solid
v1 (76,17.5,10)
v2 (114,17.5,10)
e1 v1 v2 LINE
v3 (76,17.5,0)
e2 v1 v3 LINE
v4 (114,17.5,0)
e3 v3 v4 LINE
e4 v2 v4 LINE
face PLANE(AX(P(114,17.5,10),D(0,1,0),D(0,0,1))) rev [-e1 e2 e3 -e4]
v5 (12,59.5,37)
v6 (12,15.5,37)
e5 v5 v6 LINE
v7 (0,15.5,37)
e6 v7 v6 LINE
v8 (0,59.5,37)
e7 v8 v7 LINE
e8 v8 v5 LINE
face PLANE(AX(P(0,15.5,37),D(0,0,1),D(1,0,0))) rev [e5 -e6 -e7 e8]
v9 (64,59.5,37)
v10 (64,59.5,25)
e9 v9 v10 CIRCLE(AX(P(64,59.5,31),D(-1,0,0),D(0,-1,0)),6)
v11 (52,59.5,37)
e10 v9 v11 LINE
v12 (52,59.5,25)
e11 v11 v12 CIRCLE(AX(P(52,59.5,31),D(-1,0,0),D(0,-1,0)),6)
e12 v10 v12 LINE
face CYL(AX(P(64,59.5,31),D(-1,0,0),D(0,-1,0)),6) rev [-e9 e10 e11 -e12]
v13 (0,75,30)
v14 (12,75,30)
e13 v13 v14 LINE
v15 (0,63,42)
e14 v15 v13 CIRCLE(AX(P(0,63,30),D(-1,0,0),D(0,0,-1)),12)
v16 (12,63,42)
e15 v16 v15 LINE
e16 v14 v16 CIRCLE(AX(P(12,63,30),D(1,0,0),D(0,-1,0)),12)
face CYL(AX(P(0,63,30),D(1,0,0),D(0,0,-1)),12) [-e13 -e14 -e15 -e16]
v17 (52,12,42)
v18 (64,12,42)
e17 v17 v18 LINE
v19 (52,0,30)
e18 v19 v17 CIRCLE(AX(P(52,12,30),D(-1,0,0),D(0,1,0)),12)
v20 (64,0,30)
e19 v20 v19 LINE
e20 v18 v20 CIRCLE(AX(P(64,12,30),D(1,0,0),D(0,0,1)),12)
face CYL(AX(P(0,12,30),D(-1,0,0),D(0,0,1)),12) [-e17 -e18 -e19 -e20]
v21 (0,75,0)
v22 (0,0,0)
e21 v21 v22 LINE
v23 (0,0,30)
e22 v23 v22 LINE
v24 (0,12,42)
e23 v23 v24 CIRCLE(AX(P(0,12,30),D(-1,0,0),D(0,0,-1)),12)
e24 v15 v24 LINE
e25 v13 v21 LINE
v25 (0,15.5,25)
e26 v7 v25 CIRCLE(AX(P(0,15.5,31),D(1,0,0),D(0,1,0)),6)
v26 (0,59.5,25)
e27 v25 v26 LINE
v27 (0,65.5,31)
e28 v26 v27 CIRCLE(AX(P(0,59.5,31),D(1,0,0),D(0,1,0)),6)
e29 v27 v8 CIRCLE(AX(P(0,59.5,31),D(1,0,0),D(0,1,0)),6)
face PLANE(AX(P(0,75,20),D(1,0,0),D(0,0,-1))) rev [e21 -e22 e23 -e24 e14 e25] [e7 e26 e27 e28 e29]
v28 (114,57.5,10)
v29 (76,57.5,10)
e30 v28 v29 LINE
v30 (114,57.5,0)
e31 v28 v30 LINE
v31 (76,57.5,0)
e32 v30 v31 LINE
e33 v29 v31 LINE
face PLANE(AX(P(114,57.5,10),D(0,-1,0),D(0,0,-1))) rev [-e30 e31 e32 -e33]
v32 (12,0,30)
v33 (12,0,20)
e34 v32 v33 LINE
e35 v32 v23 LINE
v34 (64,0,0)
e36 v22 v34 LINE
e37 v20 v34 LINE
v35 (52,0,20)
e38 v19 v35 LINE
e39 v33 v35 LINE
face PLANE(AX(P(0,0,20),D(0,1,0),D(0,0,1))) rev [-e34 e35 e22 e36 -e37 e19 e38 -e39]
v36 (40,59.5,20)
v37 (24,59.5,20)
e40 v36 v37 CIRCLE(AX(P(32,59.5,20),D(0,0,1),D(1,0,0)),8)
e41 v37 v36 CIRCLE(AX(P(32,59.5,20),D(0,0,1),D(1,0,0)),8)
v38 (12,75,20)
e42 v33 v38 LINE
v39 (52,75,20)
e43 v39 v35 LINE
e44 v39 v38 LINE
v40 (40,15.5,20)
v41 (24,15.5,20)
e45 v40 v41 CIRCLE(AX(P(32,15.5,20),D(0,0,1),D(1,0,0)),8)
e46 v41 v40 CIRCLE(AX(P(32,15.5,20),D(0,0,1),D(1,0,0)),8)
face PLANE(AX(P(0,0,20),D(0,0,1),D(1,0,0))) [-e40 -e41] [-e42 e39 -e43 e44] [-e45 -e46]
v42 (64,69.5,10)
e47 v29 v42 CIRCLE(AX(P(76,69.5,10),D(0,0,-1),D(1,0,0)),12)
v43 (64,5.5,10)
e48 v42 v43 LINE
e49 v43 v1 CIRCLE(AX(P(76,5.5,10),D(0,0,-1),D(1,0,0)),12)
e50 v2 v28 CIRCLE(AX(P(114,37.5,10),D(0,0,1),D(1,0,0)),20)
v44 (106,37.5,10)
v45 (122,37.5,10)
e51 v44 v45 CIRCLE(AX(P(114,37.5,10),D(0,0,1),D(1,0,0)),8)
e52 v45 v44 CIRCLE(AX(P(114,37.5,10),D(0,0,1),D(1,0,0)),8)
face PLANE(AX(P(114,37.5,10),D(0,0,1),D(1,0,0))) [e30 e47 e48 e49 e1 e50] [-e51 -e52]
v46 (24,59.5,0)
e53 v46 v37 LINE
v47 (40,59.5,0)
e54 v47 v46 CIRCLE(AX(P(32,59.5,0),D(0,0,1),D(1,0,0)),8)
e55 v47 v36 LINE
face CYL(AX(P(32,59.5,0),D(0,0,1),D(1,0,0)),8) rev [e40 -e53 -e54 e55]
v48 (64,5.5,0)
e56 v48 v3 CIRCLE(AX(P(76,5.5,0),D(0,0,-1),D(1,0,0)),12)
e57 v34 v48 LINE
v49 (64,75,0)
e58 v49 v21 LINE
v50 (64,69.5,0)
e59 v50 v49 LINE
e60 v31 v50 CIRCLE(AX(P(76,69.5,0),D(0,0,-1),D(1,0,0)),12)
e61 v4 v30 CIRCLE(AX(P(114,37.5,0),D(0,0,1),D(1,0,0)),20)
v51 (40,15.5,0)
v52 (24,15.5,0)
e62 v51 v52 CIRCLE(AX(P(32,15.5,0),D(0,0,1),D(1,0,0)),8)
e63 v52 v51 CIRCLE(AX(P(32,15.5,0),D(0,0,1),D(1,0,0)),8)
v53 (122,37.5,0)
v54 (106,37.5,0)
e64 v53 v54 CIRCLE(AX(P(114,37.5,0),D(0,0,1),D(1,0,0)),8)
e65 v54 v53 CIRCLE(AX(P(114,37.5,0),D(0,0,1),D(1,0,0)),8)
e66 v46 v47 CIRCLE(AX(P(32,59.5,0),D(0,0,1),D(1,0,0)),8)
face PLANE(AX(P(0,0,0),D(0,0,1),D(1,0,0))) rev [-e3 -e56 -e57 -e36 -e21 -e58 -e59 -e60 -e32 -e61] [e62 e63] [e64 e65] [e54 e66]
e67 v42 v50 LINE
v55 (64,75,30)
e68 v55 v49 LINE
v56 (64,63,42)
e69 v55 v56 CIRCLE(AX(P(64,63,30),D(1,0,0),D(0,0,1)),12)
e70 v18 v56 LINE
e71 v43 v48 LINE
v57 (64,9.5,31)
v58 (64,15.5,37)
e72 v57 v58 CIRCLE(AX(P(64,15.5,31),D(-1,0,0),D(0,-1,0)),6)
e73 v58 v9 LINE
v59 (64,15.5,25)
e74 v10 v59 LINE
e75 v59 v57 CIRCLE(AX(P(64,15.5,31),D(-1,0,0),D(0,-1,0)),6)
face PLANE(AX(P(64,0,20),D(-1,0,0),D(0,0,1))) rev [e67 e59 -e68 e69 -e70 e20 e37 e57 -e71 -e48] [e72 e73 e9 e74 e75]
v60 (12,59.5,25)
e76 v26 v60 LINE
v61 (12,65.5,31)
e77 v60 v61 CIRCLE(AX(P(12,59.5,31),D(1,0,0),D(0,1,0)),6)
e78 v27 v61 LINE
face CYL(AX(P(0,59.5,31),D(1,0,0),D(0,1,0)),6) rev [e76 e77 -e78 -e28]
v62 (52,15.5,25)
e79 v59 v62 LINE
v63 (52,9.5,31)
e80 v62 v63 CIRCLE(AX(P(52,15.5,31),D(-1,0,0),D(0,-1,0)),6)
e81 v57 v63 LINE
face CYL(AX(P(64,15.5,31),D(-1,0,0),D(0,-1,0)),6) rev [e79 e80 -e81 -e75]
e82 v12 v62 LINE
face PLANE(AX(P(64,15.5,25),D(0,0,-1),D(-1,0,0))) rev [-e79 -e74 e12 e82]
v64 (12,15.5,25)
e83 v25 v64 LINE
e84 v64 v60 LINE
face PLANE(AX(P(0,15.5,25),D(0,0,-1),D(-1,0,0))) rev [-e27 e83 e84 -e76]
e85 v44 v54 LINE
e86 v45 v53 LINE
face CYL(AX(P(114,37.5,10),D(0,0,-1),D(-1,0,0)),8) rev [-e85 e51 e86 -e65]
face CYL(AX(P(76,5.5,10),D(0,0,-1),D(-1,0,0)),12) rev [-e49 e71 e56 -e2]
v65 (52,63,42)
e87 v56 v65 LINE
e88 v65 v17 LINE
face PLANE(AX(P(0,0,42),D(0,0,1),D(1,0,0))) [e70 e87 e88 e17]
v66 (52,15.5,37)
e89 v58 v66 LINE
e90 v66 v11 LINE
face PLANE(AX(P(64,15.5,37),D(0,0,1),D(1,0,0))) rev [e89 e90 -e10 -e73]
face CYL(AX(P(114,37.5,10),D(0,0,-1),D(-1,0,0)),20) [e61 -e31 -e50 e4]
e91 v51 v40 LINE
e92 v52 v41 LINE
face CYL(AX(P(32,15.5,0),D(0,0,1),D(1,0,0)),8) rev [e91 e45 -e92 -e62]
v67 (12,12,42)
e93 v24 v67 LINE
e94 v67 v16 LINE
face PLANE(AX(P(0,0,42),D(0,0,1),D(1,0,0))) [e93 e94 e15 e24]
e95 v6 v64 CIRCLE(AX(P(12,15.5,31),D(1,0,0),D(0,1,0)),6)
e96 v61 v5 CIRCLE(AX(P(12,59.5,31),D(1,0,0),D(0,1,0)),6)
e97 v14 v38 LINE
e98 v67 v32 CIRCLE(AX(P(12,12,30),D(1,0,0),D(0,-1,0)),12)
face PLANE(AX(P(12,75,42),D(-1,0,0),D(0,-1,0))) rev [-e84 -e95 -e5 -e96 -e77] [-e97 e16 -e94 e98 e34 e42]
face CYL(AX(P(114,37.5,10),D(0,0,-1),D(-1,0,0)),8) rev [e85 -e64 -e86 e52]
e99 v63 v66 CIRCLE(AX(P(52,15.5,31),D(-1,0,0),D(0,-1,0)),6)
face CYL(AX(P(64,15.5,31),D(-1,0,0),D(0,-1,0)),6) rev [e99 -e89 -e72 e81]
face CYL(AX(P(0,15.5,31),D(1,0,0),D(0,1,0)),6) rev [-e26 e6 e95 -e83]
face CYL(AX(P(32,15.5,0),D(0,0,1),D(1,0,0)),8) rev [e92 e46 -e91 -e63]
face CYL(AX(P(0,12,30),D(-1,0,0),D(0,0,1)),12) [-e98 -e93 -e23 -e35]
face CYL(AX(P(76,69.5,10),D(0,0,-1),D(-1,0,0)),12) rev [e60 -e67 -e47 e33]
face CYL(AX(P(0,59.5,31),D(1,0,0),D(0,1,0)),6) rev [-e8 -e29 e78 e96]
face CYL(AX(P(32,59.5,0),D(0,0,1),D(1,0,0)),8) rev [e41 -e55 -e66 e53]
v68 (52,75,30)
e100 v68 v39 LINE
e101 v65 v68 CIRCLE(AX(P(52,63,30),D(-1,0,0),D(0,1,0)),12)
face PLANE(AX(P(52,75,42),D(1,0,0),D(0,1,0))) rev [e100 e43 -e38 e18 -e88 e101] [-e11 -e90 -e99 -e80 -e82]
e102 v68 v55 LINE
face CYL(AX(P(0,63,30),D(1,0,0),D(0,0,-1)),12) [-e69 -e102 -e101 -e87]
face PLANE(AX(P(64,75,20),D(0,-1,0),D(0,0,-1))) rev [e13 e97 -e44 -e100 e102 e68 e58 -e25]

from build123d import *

# Parameters (mm, degrees)
BASE_BLOCK_SKETCH_W     = 64
BASE_BLOCK_SKETCH_H     = 75
BASE_BLOCK_DEPTH        = 20
CLAMP_LUG_A_SKETCH_W    = 12
CLAMP_LUG_A_SKETCH_H    = 75
CLAMP_LUG_A_DEPTH       = 22
CLAMP_LUG_B_SKETCH_W    = 12
CLAMP_LUG_B_SKETCH_H    = 75
CLAMP_LUG_B_DEPTH       = 22
ADJUSTMENT_SLOT_A_DEPTH = 101.463923873
ADJUSTMENT_SLOT_B_DEPTH = 101.463923873
MOUNTING_TAB_SKETCH_R   = 8
MOUNTING_TAB_DEPTH      = 10
BACK_WALL_CUT_SKETCH_R  = 8
BACK_WALL_CUT_DEPTH     = 156.128978595
LUG_A_EDGE_FILLET_R12_R = 12
LUG_B_EDGE_FILLET_R12_R = 12


with BuildPart() as part:
    # Base Block Sketch → Base Block (new body)
    with BuildSketch(Plane.XY):
        with Locations((32, 37.5)):
            Rectangle(BASE_BLOCK_SKETCH_W, BASE_BLOCK_SKETCH_H)
    extrude(amount=BASE_BLOCK_DEPTH)

    # Clamp Lug A Sketch → Clamp Lug A (add)
    with BuildSketch(Plane.XY.offset(20)):
        with Locations((6, 37.5)):
            Rectangle(CLAMP_LUG_A_SKETCH_W, CLAMP_LUG_A_SKETCH_H)
    extrude(amount=CLAMP_LUG_A_DEPTH)

    # Clamp Lug B Sketch → Clamp Lug B (add)
    with BuildSketch(Plane.XY.offset(20)):
        with Locations((58, 37.5)):
            Rectangle(CLAMP_LUG_B_SKETCH_W, CLAMP_LUG_B_SKETCH_H)
    extrude(amount=CLAMP_LUG_B_DEPTH)

    # Adjustment Slot A Sketch → Adjustment Slot A (cut, through all)
    with BuildSketch(Plane(origin=(12, 0, 0), x_dir=(0, 0, -1), z_dir=(1, 0, 0))):
        with BuildLine():
            Line((-37, 15.5), (-37, 59.5))
            ThreePointArc((-37, 59.5), (-31, 65.5), (-25, 59.5))
            Line((-25, 59.5), (-25, 15.5))
            ThreePointArc((-25, 15.5), (-31, 9.5), (-37, 15.5))
        make_face()
    extrude(amount=-ADJUSTMENT_SLOT_A_DEPTH, mode=Mode.SUBTRACT)

    # Adjustment Slot B Sketch → Adjustment Slot B (cut, through all)
    with BuildSketch(Plane.ZY.offset(-52)):
        with BuildLine():
            Line((25, 15.5), (25, 59.5))
            ThreePointArc((25, 59.5), (31, 65.5), (37, 59.5))
            Line((37, 59.5), (37, 15.5))
            ThreePointArc((37, 15.5), (31, 9.5), (25, 15.5))
        make_face()
    extrude(amount=-ADJUSTMENT_SLOT_B_DEPTH, mode=Mode.SUBTRACT)

    # Mounting Tab Sketch → Mounting Tab (add)
    with BuildSketch(Plane.XY):
        with BuildLine():
            Line((114, 57.5), (76, 57.5))
            ThreePointArc((76, 57.5), (67.514718626, 61.014718626), (64, 69.5))
            Line((64, 69.5), (64, 5.5))
            ThreePointArc((64, 5.5), (67.514718626, 13.985281374), (76, 17.5))
            Line((76, 17.5), (114, 17.5))
            ThreePointArc((114, 17.5), (134, 37.5), (114, 57.5))
        make_face()
        with Locations((114, 37.5)):
            Circle(MOUNTING_TAB_SKETCH_R, mode=Mode.SUBTRACT)
    extrude(amount=MOUNTING_TAB_DEPTH)

    # Back Wall Cut Sketch → Back Wall Cut (cut, through all)
    with BuildSketch(Plane.XY.offset(20)):
        with Locations((32, 59.5)):
            Circle(BACK_WALL_CUT_SKETCH_R)
        with Locations((32, 15.5)):
            Circle(BACK_WALL_CUT_SKETCH_R)
    extrude(amount=-BACK_WALL_CUT_DEPTH, mode=Mode.SUBTRACT)

    # Lug A Edge Fillet R12
    lug_a_edge_fillet_r12_edges = [part.edges().sort_by_distance(p)[0] for p in [
        (6, 0, 42),
        (6, 75, 42),
    ]]
    fillet(lug_a_edge_fillet_r12_edges, radius=LUG_A_EDGE_FILLET_R12_R)

    # Lug B Edge Fillet R12
    lug_b_edge_fillet_r12_edges = [part.edges().sort_by_distance(p)[0] for p in [
        (58, 0, 42),
        (58, 75, 42),
    ]]
    fillet(lug_b_edge_fillet_r12_edges, radius=LUG_B_EDGE_FILLET_R12_R)


solid = part.part
